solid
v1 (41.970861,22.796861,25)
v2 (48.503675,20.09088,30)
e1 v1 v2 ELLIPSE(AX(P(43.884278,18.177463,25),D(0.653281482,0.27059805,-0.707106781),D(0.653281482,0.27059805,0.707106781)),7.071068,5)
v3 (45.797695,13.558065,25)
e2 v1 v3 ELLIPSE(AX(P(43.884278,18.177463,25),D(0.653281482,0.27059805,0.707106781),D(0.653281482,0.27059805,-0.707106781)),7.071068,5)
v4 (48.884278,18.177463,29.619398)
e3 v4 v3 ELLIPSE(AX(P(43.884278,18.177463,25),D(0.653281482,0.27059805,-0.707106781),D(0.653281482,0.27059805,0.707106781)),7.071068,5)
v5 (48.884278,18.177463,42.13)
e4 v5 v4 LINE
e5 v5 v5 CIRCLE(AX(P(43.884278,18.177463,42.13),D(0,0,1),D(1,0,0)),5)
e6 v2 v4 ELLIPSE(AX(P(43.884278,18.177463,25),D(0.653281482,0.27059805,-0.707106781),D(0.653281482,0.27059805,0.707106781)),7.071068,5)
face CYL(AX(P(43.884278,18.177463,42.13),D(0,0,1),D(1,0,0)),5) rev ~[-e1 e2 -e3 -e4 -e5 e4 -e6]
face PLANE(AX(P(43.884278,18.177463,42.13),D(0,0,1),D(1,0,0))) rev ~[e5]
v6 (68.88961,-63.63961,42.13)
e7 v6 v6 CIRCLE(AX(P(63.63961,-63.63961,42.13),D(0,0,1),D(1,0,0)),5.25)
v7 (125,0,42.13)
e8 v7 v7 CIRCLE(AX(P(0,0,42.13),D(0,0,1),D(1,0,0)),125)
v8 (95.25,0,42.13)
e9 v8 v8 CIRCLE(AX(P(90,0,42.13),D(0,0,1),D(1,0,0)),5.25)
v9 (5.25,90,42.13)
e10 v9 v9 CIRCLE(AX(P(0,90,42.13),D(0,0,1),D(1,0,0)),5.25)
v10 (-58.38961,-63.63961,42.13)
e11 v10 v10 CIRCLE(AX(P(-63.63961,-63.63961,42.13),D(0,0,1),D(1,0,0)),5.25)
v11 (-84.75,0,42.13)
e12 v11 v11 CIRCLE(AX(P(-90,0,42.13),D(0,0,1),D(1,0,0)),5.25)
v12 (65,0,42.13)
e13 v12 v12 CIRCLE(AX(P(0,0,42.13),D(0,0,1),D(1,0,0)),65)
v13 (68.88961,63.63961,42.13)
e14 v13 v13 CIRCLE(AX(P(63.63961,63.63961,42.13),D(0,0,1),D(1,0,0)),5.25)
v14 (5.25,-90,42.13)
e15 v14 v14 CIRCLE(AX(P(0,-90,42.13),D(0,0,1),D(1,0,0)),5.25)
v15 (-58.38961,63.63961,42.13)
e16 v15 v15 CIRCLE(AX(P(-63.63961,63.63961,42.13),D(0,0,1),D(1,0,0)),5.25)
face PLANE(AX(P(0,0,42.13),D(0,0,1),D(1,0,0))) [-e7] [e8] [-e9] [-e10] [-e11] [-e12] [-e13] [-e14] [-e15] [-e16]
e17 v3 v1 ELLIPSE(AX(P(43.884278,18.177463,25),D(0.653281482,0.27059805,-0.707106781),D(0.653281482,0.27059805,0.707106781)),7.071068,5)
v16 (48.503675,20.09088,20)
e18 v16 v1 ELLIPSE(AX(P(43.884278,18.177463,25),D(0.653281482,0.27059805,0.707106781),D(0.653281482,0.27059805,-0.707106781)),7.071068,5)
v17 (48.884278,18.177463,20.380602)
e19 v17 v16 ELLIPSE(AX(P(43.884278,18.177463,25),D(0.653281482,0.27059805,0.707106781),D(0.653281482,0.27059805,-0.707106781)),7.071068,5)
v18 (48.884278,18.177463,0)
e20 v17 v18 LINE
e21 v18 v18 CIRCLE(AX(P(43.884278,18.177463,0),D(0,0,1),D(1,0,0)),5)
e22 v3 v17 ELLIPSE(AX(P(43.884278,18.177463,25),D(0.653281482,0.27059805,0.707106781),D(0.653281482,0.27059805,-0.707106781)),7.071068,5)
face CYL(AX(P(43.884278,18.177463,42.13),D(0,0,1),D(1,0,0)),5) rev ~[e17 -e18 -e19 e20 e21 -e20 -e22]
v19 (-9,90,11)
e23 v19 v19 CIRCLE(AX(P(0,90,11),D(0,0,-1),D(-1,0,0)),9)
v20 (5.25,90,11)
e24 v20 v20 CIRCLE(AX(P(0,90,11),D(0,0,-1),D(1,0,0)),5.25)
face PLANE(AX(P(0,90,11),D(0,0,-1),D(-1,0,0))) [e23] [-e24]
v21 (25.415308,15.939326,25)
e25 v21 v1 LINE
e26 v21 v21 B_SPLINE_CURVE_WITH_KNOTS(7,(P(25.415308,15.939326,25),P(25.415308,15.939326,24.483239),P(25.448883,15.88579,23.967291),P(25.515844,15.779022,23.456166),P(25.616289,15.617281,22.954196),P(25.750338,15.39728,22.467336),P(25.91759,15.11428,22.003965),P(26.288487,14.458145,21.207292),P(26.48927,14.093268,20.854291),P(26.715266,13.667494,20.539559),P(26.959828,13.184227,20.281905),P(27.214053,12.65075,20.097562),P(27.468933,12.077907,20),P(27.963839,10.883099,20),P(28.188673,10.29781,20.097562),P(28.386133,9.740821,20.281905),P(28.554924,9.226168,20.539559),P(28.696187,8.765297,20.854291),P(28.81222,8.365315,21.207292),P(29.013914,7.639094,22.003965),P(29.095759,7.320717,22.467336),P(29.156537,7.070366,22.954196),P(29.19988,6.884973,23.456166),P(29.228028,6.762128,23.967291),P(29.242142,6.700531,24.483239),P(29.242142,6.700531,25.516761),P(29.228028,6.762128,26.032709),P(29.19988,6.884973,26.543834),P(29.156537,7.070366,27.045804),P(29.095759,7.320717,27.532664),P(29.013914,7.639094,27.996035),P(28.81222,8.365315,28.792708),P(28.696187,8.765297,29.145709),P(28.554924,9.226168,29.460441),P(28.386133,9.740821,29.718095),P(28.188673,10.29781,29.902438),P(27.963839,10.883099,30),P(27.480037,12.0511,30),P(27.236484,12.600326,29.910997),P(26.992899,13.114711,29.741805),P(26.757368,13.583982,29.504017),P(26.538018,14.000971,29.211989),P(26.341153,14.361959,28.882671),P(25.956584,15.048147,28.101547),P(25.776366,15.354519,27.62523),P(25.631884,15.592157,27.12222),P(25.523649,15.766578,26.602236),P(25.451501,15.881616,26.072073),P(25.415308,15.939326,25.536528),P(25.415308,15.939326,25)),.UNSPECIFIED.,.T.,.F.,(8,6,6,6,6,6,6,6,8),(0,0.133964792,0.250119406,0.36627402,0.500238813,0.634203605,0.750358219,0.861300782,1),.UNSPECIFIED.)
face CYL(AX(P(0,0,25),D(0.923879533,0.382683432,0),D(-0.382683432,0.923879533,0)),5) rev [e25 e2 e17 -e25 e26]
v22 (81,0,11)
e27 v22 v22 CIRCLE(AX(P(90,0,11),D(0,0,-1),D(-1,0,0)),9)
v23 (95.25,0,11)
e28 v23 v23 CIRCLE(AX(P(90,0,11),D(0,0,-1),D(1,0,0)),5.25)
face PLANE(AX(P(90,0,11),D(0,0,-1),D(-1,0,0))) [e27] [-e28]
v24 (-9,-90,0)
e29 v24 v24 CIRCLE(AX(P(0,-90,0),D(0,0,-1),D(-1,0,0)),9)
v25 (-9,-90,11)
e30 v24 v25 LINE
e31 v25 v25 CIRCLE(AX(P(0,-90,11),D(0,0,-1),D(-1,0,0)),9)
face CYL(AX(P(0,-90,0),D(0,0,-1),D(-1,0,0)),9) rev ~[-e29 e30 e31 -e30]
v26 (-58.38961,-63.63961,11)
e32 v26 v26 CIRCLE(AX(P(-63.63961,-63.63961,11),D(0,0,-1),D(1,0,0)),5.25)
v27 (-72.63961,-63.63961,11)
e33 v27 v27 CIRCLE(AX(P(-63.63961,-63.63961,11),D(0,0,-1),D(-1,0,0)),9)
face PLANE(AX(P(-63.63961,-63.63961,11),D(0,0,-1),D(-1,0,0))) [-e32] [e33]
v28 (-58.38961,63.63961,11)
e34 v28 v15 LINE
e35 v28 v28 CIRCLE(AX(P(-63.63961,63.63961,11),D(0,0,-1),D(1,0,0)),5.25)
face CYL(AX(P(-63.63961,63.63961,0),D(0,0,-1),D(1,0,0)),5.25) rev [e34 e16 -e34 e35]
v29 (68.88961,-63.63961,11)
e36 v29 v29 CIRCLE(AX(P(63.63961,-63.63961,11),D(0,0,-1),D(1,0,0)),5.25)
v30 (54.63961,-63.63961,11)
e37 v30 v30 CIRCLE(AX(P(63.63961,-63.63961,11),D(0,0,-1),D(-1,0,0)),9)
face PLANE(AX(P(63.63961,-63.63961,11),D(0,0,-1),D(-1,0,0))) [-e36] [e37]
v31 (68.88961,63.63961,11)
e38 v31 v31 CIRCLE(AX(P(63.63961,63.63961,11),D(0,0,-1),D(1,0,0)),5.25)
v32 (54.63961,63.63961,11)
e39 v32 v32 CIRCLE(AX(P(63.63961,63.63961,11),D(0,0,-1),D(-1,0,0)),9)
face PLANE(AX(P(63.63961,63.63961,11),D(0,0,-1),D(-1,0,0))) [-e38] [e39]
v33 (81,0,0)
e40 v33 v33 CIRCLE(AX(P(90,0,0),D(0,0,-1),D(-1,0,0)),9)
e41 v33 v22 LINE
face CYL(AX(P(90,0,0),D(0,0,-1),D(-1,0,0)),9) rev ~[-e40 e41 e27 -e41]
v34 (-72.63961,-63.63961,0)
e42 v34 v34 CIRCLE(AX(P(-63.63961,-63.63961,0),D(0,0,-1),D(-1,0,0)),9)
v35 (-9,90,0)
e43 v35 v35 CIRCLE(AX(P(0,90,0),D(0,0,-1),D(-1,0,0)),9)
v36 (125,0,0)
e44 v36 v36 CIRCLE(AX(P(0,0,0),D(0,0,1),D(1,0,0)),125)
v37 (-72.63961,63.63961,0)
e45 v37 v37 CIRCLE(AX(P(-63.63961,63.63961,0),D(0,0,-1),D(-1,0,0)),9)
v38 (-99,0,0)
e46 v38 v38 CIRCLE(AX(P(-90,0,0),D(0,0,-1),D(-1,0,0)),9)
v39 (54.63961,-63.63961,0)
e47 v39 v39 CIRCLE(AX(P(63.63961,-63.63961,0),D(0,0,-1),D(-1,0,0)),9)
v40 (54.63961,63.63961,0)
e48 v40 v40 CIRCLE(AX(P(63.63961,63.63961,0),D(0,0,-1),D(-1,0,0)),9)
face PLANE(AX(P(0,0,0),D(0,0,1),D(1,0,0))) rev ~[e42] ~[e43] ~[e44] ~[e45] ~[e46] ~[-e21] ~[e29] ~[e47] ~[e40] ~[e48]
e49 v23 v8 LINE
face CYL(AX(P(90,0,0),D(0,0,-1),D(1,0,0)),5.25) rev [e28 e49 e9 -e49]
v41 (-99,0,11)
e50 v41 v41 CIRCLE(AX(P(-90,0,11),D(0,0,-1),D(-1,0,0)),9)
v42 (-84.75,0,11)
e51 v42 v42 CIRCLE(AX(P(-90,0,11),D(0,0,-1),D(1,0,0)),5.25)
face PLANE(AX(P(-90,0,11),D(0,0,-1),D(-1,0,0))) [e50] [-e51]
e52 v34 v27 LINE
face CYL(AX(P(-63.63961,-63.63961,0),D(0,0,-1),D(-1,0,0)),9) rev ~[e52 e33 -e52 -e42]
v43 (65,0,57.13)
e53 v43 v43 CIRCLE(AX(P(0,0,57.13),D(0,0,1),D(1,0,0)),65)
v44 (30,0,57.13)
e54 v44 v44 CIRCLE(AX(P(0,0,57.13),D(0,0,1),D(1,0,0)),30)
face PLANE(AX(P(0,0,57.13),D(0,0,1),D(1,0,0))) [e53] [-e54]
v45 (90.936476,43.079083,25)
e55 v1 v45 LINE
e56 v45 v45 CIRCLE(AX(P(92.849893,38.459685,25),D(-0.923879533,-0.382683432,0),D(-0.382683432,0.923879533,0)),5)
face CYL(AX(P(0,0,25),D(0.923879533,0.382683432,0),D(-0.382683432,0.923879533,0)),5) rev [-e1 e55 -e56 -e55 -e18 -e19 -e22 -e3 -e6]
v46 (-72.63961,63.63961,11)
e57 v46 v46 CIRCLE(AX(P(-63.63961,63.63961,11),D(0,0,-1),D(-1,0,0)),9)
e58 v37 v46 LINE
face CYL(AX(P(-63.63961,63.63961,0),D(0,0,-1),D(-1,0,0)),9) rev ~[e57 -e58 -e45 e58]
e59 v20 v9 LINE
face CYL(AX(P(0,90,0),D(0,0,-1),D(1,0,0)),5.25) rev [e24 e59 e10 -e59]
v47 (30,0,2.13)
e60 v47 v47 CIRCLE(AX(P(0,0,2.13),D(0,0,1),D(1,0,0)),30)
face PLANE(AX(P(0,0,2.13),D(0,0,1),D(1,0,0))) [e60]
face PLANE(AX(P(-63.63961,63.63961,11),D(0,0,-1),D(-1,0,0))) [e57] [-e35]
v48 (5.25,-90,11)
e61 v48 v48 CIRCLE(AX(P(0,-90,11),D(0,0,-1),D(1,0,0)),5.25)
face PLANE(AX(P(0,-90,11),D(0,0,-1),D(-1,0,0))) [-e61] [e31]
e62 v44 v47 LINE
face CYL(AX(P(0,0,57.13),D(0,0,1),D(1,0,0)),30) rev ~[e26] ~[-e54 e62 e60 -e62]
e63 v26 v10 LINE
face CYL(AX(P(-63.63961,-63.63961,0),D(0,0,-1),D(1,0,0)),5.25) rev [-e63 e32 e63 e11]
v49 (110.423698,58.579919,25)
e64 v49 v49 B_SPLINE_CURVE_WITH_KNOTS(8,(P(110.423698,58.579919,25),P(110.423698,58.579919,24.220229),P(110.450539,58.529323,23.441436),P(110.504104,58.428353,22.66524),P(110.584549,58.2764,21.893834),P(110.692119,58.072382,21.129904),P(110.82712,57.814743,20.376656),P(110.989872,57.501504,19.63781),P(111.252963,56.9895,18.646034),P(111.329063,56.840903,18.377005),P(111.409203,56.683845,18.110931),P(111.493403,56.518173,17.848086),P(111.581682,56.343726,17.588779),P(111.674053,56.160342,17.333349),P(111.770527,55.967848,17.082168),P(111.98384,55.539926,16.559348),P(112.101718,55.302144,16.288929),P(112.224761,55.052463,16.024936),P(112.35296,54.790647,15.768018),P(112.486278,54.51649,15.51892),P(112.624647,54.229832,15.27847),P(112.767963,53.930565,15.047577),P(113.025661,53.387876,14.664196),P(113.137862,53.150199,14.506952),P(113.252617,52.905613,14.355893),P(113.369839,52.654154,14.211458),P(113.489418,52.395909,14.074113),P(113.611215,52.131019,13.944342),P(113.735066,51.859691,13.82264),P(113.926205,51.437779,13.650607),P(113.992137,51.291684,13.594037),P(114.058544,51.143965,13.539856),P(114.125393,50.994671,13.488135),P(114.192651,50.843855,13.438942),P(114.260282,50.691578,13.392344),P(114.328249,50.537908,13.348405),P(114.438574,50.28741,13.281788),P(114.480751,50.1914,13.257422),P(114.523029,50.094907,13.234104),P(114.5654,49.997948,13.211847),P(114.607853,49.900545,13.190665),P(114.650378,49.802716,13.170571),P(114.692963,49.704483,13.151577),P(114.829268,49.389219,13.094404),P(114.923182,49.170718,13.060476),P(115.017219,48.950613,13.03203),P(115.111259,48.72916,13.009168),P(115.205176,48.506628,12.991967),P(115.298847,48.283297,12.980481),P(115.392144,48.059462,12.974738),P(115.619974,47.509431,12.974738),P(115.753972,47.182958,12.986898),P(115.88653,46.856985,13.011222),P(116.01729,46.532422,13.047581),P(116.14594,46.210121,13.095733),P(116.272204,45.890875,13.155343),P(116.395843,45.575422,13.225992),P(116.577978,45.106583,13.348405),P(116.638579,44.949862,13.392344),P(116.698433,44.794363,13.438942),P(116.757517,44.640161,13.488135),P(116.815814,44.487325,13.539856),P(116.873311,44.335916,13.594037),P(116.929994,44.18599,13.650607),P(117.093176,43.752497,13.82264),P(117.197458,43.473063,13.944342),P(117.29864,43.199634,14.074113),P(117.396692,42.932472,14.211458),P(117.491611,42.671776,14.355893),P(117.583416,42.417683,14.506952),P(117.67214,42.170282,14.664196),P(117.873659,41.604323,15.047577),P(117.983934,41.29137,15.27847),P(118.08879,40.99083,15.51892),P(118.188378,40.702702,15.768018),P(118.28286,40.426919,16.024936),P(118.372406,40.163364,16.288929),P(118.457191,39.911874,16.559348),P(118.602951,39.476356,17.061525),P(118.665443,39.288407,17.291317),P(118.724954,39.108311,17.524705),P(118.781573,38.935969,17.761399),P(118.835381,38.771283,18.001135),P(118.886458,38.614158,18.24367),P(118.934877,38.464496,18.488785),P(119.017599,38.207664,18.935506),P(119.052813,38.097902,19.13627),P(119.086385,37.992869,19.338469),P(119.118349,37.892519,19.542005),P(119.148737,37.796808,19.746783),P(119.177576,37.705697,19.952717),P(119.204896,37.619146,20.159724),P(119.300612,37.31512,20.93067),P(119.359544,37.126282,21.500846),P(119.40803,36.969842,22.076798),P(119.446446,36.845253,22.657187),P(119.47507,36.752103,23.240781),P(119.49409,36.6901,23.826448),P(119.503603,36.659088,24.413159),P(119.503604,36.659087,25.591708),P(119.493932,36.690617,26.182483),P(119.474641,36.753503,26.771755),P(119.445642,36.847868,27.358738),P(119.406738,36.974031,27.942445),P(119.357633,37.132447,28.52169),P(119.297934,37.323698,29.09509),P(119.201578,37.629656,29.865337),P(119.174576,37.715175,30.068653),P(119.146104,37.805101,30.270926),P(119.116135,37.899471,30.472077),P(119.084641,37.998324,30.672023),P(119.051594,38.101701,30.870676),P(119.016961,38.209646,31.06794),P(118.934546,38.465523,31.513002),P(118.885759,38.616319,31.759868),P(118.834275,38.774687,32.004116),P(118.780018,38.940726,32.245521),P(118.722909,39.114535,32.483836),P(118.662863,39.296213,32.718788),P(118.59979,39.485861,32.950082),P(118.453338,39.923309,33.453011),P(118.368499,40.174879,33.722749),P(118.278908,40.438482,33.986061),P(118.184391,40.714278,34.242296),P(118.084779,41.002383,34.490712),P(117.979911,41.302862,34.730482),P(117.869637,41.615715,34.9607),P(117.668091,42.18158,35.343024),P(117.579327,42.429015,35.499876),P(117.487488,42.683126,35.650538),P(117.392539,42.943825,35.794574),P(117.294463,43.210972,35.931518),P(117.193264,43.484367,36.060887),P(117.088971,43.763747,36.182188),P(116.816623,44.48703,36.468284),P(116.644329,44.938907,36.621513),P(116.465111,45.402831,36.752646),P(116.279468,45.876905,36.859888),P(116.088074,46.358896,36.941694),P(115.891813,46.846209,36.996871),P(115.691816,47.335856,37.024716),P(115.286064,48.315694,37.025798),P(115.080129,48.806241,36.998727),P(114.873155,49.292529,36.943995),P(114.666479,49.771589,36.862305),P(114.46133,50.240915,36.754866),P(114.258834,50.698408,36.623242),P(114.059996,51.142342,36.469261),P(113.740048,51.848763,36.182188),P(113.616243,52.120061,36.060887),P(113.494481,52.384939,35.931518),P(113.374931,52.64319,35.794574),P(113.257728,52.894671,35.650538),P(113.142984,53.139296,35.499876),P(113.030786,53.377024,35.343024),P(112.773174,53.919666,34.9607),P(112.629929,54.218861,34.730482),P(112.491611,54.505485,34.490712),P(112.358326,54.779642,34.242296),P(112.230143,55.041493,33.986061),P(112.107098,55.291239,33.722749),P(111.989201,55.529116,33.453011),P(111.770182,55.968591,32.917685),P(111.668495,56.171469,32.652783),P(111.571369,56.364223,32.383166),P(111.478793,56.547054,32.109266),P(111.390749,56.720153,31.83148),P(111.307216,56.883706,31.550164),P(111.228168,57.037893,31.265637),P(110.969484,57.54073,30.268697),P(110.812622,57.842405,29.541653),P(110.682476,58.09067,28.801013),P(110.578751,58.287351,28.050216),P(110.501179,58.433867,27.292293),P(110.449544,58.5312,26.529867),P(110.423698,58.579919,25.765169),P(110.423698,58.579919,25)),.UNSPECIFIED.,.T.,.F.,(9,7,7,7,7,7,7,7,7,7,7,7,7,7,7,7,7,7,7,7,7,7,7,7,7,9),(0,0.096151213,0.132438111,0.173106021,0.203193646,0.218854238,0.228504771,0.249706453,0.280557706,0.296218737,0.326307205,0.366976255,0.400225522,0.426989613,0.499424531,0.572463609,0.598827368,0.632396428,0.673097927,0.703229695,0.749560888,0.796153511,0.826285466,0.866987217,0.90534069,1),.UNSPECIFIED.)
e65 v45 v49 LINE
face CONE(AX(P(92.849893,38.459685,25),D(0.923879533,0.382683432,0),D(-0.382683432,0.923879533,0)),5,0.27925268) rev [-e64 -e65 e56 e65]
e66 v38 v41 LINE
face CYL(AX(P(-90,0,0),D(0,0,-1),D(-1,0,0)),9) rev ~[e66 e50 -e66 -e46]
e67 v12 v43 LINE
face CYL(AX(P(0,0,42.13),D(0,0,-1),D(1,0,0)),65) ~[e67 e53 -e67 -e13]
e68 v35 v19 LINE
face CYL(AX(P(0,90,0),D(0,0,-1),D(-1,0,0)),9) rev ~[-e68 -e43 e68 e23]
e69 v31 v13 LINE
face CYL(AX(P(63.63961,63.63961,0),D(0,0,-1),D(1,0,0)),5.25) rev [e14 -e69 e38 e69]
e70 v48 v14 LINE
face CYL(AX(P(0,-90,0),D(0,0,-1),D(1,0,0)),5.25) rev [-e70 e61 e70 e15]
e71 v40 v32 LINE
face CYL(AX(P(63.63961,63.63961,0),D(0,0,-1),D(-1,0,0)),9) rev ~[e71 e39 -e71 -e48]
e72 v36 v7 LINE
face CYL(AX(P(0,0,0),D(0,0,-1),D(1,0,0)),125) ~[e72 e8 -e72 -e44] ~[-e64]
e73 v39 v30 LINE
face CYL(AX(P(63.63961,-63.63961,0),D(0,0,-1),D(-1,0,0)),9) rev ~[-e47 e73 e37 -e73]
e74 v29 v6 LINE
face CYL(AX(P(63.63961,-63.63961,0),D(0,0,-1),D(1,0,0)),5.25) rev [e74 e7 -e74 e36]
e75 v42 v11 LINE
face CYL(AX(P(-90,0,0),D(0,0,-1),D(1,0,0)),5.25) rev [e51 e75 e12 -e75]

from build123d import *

# Parameters (mm, degrees)
SKETCH_1_R          = 125
SKETCH_1_R_2        = 5.25
EXTRUDE_1_DEPTH     = 42.13
SKETCH_2_R          = 65
EXTRUDE_2_DEPTH     = 15
SKETCH_3_R          = 30
CUT_EXTRUDE_1_DEPTH = 55
SKETCH_6_R          = 5
CUT_EXTRUDE_2_DEPTH = 50
SKETCH_7_R          = 9
CUT_EXTRUDE_3_DEPTH = 11


with BuildPart() as part:
    # 草图1 → 凸台-拉伸1 (new body)
    with BuildSketch(Plane.XY):
        Circle(SKETCH_1_R)
        with Locations((0, 90)):
            Circle(SKETCH_1_R_2, mode=Mode.SUBTRACT)
        with Locations((63.639610307, 63.639610307)):
            Circle(SKETCH_1_R_2, mode=Mode.SUBTRACT)
        with Locations((90, 0)):
            Circle(SKETCH_1_R_2, mode=Mode.SUBTRACT)
        with Locations((63.639610307, -63.639610307)):
            Circle(SKETCH_1_R_2, mode=Mode.SUBTRACT)
        with Locations((0, -90)):
            Circle(SKETCH_1_R_2, mode=Mode.SUBTRACT)
        with Locations((-63.639610307, -63.639610307)):
            Circle(SKETCH_1_R_2, mode=Mode.SUBTRACT)
        with Locations((-90, 0)):
            Circle(SKETCH_1_R_2, mode=Mode.SUBTRACT)
        with Locations((-63.639610307, 63.639610307)):
            Circle(SKETCH_1_R_2, mode=Mode.SUBTRACT)
    extrude(amount=EXTRUDE_1_DEPTH)

    # 草图2 → 凸台-拉伸2 (add)
    with BuildSketch(Plane.XY.offset(42.13)):
        Circle(SKETCH_2_R)
    extrude(amount=EXTRUDE_2_DEPTH)

    # 草图3 → 切除-拉伸1 (cut)
    with BuildSketch(Plane.XY.offset(57.13)):
        Circle(SKETCH_3_R)
    extrude(amount=-CUT_EXTRUDE_1_DEPTH, mode=Mode.SUBTRACT)

    # 草图5 → 切除-旋转1 (revolve, cut)
    with BuildSketch(Plane(origin=(0, 0, 0), x_dir=(0, 0, 1), z_dir=(-0.3826834323650906, 0.9238795325112865, 0)), mode=Mode.PRIVATE) as cut_revolve_1_sk:
        Polygon((30, 100.5), (37.70842723, 127.382480462), (25, 127.382480462), (25, 124.917518293), (25, 0), (30, 0), align=None)
    revolve(cut_revolve_1_sk.sketch.rotate(Axis((123.47749494, 51.146053052, 25), (-0.9238795325112864, -0.3826834323650906, 0)), 90), axis=Axis((123.47749494, 51.146053052, 25), (-0.9238795325112864, -0.3826834323650906, 0)), mode=Mode.SUBTRACT)

    # 草图6 → 切除-拉伸2 (cut)
    with BuildSketch(Plane.XY.offset(42.13)):
        with Locations((43.884277794, 18.177463037)):
            Circle(SKETCH_6_R)
    extrude(amount=-CUT_EXTRUDE_2_DEPTH, mode=Mode.SUBTRACT)

    # 草图7 → 切除-拉伸3 (cut)
    with BuildSketch(Plane(origin=(0, 0, 0), x_dir=(-1, 0, 0), z_dir=(0, 0, -1))):
        with Locations((0, 90)):
            Circle(SKETCH_7_R)
        with Locations((63.639610307, 63.639610307)):
            Circle(SKETCH_7_R)
        with Locations((90, 0)):
            Circle(SKETCH_7_R)
        with Locations((63.639610307, -63.639610307)):
            Circle(SKETCH_7_R)
        with Locations((0, -90)):
            Circle(SKETCH_7_R)
        with Locations((-63.639610307, -63.639610307)):
            Circle(SKETCH_7_R)
        with Locations((-90, 0)):
            Circle(SKETCH_7_R)
        with Locations((-63.639610307, 63.639610307)):
            Circle(SKETCH_7_R)
    extrude(amount=-CUT_EXTRUDE_3_DEPTH, mode=Mode.SUBTRACT)


solid = part.part
